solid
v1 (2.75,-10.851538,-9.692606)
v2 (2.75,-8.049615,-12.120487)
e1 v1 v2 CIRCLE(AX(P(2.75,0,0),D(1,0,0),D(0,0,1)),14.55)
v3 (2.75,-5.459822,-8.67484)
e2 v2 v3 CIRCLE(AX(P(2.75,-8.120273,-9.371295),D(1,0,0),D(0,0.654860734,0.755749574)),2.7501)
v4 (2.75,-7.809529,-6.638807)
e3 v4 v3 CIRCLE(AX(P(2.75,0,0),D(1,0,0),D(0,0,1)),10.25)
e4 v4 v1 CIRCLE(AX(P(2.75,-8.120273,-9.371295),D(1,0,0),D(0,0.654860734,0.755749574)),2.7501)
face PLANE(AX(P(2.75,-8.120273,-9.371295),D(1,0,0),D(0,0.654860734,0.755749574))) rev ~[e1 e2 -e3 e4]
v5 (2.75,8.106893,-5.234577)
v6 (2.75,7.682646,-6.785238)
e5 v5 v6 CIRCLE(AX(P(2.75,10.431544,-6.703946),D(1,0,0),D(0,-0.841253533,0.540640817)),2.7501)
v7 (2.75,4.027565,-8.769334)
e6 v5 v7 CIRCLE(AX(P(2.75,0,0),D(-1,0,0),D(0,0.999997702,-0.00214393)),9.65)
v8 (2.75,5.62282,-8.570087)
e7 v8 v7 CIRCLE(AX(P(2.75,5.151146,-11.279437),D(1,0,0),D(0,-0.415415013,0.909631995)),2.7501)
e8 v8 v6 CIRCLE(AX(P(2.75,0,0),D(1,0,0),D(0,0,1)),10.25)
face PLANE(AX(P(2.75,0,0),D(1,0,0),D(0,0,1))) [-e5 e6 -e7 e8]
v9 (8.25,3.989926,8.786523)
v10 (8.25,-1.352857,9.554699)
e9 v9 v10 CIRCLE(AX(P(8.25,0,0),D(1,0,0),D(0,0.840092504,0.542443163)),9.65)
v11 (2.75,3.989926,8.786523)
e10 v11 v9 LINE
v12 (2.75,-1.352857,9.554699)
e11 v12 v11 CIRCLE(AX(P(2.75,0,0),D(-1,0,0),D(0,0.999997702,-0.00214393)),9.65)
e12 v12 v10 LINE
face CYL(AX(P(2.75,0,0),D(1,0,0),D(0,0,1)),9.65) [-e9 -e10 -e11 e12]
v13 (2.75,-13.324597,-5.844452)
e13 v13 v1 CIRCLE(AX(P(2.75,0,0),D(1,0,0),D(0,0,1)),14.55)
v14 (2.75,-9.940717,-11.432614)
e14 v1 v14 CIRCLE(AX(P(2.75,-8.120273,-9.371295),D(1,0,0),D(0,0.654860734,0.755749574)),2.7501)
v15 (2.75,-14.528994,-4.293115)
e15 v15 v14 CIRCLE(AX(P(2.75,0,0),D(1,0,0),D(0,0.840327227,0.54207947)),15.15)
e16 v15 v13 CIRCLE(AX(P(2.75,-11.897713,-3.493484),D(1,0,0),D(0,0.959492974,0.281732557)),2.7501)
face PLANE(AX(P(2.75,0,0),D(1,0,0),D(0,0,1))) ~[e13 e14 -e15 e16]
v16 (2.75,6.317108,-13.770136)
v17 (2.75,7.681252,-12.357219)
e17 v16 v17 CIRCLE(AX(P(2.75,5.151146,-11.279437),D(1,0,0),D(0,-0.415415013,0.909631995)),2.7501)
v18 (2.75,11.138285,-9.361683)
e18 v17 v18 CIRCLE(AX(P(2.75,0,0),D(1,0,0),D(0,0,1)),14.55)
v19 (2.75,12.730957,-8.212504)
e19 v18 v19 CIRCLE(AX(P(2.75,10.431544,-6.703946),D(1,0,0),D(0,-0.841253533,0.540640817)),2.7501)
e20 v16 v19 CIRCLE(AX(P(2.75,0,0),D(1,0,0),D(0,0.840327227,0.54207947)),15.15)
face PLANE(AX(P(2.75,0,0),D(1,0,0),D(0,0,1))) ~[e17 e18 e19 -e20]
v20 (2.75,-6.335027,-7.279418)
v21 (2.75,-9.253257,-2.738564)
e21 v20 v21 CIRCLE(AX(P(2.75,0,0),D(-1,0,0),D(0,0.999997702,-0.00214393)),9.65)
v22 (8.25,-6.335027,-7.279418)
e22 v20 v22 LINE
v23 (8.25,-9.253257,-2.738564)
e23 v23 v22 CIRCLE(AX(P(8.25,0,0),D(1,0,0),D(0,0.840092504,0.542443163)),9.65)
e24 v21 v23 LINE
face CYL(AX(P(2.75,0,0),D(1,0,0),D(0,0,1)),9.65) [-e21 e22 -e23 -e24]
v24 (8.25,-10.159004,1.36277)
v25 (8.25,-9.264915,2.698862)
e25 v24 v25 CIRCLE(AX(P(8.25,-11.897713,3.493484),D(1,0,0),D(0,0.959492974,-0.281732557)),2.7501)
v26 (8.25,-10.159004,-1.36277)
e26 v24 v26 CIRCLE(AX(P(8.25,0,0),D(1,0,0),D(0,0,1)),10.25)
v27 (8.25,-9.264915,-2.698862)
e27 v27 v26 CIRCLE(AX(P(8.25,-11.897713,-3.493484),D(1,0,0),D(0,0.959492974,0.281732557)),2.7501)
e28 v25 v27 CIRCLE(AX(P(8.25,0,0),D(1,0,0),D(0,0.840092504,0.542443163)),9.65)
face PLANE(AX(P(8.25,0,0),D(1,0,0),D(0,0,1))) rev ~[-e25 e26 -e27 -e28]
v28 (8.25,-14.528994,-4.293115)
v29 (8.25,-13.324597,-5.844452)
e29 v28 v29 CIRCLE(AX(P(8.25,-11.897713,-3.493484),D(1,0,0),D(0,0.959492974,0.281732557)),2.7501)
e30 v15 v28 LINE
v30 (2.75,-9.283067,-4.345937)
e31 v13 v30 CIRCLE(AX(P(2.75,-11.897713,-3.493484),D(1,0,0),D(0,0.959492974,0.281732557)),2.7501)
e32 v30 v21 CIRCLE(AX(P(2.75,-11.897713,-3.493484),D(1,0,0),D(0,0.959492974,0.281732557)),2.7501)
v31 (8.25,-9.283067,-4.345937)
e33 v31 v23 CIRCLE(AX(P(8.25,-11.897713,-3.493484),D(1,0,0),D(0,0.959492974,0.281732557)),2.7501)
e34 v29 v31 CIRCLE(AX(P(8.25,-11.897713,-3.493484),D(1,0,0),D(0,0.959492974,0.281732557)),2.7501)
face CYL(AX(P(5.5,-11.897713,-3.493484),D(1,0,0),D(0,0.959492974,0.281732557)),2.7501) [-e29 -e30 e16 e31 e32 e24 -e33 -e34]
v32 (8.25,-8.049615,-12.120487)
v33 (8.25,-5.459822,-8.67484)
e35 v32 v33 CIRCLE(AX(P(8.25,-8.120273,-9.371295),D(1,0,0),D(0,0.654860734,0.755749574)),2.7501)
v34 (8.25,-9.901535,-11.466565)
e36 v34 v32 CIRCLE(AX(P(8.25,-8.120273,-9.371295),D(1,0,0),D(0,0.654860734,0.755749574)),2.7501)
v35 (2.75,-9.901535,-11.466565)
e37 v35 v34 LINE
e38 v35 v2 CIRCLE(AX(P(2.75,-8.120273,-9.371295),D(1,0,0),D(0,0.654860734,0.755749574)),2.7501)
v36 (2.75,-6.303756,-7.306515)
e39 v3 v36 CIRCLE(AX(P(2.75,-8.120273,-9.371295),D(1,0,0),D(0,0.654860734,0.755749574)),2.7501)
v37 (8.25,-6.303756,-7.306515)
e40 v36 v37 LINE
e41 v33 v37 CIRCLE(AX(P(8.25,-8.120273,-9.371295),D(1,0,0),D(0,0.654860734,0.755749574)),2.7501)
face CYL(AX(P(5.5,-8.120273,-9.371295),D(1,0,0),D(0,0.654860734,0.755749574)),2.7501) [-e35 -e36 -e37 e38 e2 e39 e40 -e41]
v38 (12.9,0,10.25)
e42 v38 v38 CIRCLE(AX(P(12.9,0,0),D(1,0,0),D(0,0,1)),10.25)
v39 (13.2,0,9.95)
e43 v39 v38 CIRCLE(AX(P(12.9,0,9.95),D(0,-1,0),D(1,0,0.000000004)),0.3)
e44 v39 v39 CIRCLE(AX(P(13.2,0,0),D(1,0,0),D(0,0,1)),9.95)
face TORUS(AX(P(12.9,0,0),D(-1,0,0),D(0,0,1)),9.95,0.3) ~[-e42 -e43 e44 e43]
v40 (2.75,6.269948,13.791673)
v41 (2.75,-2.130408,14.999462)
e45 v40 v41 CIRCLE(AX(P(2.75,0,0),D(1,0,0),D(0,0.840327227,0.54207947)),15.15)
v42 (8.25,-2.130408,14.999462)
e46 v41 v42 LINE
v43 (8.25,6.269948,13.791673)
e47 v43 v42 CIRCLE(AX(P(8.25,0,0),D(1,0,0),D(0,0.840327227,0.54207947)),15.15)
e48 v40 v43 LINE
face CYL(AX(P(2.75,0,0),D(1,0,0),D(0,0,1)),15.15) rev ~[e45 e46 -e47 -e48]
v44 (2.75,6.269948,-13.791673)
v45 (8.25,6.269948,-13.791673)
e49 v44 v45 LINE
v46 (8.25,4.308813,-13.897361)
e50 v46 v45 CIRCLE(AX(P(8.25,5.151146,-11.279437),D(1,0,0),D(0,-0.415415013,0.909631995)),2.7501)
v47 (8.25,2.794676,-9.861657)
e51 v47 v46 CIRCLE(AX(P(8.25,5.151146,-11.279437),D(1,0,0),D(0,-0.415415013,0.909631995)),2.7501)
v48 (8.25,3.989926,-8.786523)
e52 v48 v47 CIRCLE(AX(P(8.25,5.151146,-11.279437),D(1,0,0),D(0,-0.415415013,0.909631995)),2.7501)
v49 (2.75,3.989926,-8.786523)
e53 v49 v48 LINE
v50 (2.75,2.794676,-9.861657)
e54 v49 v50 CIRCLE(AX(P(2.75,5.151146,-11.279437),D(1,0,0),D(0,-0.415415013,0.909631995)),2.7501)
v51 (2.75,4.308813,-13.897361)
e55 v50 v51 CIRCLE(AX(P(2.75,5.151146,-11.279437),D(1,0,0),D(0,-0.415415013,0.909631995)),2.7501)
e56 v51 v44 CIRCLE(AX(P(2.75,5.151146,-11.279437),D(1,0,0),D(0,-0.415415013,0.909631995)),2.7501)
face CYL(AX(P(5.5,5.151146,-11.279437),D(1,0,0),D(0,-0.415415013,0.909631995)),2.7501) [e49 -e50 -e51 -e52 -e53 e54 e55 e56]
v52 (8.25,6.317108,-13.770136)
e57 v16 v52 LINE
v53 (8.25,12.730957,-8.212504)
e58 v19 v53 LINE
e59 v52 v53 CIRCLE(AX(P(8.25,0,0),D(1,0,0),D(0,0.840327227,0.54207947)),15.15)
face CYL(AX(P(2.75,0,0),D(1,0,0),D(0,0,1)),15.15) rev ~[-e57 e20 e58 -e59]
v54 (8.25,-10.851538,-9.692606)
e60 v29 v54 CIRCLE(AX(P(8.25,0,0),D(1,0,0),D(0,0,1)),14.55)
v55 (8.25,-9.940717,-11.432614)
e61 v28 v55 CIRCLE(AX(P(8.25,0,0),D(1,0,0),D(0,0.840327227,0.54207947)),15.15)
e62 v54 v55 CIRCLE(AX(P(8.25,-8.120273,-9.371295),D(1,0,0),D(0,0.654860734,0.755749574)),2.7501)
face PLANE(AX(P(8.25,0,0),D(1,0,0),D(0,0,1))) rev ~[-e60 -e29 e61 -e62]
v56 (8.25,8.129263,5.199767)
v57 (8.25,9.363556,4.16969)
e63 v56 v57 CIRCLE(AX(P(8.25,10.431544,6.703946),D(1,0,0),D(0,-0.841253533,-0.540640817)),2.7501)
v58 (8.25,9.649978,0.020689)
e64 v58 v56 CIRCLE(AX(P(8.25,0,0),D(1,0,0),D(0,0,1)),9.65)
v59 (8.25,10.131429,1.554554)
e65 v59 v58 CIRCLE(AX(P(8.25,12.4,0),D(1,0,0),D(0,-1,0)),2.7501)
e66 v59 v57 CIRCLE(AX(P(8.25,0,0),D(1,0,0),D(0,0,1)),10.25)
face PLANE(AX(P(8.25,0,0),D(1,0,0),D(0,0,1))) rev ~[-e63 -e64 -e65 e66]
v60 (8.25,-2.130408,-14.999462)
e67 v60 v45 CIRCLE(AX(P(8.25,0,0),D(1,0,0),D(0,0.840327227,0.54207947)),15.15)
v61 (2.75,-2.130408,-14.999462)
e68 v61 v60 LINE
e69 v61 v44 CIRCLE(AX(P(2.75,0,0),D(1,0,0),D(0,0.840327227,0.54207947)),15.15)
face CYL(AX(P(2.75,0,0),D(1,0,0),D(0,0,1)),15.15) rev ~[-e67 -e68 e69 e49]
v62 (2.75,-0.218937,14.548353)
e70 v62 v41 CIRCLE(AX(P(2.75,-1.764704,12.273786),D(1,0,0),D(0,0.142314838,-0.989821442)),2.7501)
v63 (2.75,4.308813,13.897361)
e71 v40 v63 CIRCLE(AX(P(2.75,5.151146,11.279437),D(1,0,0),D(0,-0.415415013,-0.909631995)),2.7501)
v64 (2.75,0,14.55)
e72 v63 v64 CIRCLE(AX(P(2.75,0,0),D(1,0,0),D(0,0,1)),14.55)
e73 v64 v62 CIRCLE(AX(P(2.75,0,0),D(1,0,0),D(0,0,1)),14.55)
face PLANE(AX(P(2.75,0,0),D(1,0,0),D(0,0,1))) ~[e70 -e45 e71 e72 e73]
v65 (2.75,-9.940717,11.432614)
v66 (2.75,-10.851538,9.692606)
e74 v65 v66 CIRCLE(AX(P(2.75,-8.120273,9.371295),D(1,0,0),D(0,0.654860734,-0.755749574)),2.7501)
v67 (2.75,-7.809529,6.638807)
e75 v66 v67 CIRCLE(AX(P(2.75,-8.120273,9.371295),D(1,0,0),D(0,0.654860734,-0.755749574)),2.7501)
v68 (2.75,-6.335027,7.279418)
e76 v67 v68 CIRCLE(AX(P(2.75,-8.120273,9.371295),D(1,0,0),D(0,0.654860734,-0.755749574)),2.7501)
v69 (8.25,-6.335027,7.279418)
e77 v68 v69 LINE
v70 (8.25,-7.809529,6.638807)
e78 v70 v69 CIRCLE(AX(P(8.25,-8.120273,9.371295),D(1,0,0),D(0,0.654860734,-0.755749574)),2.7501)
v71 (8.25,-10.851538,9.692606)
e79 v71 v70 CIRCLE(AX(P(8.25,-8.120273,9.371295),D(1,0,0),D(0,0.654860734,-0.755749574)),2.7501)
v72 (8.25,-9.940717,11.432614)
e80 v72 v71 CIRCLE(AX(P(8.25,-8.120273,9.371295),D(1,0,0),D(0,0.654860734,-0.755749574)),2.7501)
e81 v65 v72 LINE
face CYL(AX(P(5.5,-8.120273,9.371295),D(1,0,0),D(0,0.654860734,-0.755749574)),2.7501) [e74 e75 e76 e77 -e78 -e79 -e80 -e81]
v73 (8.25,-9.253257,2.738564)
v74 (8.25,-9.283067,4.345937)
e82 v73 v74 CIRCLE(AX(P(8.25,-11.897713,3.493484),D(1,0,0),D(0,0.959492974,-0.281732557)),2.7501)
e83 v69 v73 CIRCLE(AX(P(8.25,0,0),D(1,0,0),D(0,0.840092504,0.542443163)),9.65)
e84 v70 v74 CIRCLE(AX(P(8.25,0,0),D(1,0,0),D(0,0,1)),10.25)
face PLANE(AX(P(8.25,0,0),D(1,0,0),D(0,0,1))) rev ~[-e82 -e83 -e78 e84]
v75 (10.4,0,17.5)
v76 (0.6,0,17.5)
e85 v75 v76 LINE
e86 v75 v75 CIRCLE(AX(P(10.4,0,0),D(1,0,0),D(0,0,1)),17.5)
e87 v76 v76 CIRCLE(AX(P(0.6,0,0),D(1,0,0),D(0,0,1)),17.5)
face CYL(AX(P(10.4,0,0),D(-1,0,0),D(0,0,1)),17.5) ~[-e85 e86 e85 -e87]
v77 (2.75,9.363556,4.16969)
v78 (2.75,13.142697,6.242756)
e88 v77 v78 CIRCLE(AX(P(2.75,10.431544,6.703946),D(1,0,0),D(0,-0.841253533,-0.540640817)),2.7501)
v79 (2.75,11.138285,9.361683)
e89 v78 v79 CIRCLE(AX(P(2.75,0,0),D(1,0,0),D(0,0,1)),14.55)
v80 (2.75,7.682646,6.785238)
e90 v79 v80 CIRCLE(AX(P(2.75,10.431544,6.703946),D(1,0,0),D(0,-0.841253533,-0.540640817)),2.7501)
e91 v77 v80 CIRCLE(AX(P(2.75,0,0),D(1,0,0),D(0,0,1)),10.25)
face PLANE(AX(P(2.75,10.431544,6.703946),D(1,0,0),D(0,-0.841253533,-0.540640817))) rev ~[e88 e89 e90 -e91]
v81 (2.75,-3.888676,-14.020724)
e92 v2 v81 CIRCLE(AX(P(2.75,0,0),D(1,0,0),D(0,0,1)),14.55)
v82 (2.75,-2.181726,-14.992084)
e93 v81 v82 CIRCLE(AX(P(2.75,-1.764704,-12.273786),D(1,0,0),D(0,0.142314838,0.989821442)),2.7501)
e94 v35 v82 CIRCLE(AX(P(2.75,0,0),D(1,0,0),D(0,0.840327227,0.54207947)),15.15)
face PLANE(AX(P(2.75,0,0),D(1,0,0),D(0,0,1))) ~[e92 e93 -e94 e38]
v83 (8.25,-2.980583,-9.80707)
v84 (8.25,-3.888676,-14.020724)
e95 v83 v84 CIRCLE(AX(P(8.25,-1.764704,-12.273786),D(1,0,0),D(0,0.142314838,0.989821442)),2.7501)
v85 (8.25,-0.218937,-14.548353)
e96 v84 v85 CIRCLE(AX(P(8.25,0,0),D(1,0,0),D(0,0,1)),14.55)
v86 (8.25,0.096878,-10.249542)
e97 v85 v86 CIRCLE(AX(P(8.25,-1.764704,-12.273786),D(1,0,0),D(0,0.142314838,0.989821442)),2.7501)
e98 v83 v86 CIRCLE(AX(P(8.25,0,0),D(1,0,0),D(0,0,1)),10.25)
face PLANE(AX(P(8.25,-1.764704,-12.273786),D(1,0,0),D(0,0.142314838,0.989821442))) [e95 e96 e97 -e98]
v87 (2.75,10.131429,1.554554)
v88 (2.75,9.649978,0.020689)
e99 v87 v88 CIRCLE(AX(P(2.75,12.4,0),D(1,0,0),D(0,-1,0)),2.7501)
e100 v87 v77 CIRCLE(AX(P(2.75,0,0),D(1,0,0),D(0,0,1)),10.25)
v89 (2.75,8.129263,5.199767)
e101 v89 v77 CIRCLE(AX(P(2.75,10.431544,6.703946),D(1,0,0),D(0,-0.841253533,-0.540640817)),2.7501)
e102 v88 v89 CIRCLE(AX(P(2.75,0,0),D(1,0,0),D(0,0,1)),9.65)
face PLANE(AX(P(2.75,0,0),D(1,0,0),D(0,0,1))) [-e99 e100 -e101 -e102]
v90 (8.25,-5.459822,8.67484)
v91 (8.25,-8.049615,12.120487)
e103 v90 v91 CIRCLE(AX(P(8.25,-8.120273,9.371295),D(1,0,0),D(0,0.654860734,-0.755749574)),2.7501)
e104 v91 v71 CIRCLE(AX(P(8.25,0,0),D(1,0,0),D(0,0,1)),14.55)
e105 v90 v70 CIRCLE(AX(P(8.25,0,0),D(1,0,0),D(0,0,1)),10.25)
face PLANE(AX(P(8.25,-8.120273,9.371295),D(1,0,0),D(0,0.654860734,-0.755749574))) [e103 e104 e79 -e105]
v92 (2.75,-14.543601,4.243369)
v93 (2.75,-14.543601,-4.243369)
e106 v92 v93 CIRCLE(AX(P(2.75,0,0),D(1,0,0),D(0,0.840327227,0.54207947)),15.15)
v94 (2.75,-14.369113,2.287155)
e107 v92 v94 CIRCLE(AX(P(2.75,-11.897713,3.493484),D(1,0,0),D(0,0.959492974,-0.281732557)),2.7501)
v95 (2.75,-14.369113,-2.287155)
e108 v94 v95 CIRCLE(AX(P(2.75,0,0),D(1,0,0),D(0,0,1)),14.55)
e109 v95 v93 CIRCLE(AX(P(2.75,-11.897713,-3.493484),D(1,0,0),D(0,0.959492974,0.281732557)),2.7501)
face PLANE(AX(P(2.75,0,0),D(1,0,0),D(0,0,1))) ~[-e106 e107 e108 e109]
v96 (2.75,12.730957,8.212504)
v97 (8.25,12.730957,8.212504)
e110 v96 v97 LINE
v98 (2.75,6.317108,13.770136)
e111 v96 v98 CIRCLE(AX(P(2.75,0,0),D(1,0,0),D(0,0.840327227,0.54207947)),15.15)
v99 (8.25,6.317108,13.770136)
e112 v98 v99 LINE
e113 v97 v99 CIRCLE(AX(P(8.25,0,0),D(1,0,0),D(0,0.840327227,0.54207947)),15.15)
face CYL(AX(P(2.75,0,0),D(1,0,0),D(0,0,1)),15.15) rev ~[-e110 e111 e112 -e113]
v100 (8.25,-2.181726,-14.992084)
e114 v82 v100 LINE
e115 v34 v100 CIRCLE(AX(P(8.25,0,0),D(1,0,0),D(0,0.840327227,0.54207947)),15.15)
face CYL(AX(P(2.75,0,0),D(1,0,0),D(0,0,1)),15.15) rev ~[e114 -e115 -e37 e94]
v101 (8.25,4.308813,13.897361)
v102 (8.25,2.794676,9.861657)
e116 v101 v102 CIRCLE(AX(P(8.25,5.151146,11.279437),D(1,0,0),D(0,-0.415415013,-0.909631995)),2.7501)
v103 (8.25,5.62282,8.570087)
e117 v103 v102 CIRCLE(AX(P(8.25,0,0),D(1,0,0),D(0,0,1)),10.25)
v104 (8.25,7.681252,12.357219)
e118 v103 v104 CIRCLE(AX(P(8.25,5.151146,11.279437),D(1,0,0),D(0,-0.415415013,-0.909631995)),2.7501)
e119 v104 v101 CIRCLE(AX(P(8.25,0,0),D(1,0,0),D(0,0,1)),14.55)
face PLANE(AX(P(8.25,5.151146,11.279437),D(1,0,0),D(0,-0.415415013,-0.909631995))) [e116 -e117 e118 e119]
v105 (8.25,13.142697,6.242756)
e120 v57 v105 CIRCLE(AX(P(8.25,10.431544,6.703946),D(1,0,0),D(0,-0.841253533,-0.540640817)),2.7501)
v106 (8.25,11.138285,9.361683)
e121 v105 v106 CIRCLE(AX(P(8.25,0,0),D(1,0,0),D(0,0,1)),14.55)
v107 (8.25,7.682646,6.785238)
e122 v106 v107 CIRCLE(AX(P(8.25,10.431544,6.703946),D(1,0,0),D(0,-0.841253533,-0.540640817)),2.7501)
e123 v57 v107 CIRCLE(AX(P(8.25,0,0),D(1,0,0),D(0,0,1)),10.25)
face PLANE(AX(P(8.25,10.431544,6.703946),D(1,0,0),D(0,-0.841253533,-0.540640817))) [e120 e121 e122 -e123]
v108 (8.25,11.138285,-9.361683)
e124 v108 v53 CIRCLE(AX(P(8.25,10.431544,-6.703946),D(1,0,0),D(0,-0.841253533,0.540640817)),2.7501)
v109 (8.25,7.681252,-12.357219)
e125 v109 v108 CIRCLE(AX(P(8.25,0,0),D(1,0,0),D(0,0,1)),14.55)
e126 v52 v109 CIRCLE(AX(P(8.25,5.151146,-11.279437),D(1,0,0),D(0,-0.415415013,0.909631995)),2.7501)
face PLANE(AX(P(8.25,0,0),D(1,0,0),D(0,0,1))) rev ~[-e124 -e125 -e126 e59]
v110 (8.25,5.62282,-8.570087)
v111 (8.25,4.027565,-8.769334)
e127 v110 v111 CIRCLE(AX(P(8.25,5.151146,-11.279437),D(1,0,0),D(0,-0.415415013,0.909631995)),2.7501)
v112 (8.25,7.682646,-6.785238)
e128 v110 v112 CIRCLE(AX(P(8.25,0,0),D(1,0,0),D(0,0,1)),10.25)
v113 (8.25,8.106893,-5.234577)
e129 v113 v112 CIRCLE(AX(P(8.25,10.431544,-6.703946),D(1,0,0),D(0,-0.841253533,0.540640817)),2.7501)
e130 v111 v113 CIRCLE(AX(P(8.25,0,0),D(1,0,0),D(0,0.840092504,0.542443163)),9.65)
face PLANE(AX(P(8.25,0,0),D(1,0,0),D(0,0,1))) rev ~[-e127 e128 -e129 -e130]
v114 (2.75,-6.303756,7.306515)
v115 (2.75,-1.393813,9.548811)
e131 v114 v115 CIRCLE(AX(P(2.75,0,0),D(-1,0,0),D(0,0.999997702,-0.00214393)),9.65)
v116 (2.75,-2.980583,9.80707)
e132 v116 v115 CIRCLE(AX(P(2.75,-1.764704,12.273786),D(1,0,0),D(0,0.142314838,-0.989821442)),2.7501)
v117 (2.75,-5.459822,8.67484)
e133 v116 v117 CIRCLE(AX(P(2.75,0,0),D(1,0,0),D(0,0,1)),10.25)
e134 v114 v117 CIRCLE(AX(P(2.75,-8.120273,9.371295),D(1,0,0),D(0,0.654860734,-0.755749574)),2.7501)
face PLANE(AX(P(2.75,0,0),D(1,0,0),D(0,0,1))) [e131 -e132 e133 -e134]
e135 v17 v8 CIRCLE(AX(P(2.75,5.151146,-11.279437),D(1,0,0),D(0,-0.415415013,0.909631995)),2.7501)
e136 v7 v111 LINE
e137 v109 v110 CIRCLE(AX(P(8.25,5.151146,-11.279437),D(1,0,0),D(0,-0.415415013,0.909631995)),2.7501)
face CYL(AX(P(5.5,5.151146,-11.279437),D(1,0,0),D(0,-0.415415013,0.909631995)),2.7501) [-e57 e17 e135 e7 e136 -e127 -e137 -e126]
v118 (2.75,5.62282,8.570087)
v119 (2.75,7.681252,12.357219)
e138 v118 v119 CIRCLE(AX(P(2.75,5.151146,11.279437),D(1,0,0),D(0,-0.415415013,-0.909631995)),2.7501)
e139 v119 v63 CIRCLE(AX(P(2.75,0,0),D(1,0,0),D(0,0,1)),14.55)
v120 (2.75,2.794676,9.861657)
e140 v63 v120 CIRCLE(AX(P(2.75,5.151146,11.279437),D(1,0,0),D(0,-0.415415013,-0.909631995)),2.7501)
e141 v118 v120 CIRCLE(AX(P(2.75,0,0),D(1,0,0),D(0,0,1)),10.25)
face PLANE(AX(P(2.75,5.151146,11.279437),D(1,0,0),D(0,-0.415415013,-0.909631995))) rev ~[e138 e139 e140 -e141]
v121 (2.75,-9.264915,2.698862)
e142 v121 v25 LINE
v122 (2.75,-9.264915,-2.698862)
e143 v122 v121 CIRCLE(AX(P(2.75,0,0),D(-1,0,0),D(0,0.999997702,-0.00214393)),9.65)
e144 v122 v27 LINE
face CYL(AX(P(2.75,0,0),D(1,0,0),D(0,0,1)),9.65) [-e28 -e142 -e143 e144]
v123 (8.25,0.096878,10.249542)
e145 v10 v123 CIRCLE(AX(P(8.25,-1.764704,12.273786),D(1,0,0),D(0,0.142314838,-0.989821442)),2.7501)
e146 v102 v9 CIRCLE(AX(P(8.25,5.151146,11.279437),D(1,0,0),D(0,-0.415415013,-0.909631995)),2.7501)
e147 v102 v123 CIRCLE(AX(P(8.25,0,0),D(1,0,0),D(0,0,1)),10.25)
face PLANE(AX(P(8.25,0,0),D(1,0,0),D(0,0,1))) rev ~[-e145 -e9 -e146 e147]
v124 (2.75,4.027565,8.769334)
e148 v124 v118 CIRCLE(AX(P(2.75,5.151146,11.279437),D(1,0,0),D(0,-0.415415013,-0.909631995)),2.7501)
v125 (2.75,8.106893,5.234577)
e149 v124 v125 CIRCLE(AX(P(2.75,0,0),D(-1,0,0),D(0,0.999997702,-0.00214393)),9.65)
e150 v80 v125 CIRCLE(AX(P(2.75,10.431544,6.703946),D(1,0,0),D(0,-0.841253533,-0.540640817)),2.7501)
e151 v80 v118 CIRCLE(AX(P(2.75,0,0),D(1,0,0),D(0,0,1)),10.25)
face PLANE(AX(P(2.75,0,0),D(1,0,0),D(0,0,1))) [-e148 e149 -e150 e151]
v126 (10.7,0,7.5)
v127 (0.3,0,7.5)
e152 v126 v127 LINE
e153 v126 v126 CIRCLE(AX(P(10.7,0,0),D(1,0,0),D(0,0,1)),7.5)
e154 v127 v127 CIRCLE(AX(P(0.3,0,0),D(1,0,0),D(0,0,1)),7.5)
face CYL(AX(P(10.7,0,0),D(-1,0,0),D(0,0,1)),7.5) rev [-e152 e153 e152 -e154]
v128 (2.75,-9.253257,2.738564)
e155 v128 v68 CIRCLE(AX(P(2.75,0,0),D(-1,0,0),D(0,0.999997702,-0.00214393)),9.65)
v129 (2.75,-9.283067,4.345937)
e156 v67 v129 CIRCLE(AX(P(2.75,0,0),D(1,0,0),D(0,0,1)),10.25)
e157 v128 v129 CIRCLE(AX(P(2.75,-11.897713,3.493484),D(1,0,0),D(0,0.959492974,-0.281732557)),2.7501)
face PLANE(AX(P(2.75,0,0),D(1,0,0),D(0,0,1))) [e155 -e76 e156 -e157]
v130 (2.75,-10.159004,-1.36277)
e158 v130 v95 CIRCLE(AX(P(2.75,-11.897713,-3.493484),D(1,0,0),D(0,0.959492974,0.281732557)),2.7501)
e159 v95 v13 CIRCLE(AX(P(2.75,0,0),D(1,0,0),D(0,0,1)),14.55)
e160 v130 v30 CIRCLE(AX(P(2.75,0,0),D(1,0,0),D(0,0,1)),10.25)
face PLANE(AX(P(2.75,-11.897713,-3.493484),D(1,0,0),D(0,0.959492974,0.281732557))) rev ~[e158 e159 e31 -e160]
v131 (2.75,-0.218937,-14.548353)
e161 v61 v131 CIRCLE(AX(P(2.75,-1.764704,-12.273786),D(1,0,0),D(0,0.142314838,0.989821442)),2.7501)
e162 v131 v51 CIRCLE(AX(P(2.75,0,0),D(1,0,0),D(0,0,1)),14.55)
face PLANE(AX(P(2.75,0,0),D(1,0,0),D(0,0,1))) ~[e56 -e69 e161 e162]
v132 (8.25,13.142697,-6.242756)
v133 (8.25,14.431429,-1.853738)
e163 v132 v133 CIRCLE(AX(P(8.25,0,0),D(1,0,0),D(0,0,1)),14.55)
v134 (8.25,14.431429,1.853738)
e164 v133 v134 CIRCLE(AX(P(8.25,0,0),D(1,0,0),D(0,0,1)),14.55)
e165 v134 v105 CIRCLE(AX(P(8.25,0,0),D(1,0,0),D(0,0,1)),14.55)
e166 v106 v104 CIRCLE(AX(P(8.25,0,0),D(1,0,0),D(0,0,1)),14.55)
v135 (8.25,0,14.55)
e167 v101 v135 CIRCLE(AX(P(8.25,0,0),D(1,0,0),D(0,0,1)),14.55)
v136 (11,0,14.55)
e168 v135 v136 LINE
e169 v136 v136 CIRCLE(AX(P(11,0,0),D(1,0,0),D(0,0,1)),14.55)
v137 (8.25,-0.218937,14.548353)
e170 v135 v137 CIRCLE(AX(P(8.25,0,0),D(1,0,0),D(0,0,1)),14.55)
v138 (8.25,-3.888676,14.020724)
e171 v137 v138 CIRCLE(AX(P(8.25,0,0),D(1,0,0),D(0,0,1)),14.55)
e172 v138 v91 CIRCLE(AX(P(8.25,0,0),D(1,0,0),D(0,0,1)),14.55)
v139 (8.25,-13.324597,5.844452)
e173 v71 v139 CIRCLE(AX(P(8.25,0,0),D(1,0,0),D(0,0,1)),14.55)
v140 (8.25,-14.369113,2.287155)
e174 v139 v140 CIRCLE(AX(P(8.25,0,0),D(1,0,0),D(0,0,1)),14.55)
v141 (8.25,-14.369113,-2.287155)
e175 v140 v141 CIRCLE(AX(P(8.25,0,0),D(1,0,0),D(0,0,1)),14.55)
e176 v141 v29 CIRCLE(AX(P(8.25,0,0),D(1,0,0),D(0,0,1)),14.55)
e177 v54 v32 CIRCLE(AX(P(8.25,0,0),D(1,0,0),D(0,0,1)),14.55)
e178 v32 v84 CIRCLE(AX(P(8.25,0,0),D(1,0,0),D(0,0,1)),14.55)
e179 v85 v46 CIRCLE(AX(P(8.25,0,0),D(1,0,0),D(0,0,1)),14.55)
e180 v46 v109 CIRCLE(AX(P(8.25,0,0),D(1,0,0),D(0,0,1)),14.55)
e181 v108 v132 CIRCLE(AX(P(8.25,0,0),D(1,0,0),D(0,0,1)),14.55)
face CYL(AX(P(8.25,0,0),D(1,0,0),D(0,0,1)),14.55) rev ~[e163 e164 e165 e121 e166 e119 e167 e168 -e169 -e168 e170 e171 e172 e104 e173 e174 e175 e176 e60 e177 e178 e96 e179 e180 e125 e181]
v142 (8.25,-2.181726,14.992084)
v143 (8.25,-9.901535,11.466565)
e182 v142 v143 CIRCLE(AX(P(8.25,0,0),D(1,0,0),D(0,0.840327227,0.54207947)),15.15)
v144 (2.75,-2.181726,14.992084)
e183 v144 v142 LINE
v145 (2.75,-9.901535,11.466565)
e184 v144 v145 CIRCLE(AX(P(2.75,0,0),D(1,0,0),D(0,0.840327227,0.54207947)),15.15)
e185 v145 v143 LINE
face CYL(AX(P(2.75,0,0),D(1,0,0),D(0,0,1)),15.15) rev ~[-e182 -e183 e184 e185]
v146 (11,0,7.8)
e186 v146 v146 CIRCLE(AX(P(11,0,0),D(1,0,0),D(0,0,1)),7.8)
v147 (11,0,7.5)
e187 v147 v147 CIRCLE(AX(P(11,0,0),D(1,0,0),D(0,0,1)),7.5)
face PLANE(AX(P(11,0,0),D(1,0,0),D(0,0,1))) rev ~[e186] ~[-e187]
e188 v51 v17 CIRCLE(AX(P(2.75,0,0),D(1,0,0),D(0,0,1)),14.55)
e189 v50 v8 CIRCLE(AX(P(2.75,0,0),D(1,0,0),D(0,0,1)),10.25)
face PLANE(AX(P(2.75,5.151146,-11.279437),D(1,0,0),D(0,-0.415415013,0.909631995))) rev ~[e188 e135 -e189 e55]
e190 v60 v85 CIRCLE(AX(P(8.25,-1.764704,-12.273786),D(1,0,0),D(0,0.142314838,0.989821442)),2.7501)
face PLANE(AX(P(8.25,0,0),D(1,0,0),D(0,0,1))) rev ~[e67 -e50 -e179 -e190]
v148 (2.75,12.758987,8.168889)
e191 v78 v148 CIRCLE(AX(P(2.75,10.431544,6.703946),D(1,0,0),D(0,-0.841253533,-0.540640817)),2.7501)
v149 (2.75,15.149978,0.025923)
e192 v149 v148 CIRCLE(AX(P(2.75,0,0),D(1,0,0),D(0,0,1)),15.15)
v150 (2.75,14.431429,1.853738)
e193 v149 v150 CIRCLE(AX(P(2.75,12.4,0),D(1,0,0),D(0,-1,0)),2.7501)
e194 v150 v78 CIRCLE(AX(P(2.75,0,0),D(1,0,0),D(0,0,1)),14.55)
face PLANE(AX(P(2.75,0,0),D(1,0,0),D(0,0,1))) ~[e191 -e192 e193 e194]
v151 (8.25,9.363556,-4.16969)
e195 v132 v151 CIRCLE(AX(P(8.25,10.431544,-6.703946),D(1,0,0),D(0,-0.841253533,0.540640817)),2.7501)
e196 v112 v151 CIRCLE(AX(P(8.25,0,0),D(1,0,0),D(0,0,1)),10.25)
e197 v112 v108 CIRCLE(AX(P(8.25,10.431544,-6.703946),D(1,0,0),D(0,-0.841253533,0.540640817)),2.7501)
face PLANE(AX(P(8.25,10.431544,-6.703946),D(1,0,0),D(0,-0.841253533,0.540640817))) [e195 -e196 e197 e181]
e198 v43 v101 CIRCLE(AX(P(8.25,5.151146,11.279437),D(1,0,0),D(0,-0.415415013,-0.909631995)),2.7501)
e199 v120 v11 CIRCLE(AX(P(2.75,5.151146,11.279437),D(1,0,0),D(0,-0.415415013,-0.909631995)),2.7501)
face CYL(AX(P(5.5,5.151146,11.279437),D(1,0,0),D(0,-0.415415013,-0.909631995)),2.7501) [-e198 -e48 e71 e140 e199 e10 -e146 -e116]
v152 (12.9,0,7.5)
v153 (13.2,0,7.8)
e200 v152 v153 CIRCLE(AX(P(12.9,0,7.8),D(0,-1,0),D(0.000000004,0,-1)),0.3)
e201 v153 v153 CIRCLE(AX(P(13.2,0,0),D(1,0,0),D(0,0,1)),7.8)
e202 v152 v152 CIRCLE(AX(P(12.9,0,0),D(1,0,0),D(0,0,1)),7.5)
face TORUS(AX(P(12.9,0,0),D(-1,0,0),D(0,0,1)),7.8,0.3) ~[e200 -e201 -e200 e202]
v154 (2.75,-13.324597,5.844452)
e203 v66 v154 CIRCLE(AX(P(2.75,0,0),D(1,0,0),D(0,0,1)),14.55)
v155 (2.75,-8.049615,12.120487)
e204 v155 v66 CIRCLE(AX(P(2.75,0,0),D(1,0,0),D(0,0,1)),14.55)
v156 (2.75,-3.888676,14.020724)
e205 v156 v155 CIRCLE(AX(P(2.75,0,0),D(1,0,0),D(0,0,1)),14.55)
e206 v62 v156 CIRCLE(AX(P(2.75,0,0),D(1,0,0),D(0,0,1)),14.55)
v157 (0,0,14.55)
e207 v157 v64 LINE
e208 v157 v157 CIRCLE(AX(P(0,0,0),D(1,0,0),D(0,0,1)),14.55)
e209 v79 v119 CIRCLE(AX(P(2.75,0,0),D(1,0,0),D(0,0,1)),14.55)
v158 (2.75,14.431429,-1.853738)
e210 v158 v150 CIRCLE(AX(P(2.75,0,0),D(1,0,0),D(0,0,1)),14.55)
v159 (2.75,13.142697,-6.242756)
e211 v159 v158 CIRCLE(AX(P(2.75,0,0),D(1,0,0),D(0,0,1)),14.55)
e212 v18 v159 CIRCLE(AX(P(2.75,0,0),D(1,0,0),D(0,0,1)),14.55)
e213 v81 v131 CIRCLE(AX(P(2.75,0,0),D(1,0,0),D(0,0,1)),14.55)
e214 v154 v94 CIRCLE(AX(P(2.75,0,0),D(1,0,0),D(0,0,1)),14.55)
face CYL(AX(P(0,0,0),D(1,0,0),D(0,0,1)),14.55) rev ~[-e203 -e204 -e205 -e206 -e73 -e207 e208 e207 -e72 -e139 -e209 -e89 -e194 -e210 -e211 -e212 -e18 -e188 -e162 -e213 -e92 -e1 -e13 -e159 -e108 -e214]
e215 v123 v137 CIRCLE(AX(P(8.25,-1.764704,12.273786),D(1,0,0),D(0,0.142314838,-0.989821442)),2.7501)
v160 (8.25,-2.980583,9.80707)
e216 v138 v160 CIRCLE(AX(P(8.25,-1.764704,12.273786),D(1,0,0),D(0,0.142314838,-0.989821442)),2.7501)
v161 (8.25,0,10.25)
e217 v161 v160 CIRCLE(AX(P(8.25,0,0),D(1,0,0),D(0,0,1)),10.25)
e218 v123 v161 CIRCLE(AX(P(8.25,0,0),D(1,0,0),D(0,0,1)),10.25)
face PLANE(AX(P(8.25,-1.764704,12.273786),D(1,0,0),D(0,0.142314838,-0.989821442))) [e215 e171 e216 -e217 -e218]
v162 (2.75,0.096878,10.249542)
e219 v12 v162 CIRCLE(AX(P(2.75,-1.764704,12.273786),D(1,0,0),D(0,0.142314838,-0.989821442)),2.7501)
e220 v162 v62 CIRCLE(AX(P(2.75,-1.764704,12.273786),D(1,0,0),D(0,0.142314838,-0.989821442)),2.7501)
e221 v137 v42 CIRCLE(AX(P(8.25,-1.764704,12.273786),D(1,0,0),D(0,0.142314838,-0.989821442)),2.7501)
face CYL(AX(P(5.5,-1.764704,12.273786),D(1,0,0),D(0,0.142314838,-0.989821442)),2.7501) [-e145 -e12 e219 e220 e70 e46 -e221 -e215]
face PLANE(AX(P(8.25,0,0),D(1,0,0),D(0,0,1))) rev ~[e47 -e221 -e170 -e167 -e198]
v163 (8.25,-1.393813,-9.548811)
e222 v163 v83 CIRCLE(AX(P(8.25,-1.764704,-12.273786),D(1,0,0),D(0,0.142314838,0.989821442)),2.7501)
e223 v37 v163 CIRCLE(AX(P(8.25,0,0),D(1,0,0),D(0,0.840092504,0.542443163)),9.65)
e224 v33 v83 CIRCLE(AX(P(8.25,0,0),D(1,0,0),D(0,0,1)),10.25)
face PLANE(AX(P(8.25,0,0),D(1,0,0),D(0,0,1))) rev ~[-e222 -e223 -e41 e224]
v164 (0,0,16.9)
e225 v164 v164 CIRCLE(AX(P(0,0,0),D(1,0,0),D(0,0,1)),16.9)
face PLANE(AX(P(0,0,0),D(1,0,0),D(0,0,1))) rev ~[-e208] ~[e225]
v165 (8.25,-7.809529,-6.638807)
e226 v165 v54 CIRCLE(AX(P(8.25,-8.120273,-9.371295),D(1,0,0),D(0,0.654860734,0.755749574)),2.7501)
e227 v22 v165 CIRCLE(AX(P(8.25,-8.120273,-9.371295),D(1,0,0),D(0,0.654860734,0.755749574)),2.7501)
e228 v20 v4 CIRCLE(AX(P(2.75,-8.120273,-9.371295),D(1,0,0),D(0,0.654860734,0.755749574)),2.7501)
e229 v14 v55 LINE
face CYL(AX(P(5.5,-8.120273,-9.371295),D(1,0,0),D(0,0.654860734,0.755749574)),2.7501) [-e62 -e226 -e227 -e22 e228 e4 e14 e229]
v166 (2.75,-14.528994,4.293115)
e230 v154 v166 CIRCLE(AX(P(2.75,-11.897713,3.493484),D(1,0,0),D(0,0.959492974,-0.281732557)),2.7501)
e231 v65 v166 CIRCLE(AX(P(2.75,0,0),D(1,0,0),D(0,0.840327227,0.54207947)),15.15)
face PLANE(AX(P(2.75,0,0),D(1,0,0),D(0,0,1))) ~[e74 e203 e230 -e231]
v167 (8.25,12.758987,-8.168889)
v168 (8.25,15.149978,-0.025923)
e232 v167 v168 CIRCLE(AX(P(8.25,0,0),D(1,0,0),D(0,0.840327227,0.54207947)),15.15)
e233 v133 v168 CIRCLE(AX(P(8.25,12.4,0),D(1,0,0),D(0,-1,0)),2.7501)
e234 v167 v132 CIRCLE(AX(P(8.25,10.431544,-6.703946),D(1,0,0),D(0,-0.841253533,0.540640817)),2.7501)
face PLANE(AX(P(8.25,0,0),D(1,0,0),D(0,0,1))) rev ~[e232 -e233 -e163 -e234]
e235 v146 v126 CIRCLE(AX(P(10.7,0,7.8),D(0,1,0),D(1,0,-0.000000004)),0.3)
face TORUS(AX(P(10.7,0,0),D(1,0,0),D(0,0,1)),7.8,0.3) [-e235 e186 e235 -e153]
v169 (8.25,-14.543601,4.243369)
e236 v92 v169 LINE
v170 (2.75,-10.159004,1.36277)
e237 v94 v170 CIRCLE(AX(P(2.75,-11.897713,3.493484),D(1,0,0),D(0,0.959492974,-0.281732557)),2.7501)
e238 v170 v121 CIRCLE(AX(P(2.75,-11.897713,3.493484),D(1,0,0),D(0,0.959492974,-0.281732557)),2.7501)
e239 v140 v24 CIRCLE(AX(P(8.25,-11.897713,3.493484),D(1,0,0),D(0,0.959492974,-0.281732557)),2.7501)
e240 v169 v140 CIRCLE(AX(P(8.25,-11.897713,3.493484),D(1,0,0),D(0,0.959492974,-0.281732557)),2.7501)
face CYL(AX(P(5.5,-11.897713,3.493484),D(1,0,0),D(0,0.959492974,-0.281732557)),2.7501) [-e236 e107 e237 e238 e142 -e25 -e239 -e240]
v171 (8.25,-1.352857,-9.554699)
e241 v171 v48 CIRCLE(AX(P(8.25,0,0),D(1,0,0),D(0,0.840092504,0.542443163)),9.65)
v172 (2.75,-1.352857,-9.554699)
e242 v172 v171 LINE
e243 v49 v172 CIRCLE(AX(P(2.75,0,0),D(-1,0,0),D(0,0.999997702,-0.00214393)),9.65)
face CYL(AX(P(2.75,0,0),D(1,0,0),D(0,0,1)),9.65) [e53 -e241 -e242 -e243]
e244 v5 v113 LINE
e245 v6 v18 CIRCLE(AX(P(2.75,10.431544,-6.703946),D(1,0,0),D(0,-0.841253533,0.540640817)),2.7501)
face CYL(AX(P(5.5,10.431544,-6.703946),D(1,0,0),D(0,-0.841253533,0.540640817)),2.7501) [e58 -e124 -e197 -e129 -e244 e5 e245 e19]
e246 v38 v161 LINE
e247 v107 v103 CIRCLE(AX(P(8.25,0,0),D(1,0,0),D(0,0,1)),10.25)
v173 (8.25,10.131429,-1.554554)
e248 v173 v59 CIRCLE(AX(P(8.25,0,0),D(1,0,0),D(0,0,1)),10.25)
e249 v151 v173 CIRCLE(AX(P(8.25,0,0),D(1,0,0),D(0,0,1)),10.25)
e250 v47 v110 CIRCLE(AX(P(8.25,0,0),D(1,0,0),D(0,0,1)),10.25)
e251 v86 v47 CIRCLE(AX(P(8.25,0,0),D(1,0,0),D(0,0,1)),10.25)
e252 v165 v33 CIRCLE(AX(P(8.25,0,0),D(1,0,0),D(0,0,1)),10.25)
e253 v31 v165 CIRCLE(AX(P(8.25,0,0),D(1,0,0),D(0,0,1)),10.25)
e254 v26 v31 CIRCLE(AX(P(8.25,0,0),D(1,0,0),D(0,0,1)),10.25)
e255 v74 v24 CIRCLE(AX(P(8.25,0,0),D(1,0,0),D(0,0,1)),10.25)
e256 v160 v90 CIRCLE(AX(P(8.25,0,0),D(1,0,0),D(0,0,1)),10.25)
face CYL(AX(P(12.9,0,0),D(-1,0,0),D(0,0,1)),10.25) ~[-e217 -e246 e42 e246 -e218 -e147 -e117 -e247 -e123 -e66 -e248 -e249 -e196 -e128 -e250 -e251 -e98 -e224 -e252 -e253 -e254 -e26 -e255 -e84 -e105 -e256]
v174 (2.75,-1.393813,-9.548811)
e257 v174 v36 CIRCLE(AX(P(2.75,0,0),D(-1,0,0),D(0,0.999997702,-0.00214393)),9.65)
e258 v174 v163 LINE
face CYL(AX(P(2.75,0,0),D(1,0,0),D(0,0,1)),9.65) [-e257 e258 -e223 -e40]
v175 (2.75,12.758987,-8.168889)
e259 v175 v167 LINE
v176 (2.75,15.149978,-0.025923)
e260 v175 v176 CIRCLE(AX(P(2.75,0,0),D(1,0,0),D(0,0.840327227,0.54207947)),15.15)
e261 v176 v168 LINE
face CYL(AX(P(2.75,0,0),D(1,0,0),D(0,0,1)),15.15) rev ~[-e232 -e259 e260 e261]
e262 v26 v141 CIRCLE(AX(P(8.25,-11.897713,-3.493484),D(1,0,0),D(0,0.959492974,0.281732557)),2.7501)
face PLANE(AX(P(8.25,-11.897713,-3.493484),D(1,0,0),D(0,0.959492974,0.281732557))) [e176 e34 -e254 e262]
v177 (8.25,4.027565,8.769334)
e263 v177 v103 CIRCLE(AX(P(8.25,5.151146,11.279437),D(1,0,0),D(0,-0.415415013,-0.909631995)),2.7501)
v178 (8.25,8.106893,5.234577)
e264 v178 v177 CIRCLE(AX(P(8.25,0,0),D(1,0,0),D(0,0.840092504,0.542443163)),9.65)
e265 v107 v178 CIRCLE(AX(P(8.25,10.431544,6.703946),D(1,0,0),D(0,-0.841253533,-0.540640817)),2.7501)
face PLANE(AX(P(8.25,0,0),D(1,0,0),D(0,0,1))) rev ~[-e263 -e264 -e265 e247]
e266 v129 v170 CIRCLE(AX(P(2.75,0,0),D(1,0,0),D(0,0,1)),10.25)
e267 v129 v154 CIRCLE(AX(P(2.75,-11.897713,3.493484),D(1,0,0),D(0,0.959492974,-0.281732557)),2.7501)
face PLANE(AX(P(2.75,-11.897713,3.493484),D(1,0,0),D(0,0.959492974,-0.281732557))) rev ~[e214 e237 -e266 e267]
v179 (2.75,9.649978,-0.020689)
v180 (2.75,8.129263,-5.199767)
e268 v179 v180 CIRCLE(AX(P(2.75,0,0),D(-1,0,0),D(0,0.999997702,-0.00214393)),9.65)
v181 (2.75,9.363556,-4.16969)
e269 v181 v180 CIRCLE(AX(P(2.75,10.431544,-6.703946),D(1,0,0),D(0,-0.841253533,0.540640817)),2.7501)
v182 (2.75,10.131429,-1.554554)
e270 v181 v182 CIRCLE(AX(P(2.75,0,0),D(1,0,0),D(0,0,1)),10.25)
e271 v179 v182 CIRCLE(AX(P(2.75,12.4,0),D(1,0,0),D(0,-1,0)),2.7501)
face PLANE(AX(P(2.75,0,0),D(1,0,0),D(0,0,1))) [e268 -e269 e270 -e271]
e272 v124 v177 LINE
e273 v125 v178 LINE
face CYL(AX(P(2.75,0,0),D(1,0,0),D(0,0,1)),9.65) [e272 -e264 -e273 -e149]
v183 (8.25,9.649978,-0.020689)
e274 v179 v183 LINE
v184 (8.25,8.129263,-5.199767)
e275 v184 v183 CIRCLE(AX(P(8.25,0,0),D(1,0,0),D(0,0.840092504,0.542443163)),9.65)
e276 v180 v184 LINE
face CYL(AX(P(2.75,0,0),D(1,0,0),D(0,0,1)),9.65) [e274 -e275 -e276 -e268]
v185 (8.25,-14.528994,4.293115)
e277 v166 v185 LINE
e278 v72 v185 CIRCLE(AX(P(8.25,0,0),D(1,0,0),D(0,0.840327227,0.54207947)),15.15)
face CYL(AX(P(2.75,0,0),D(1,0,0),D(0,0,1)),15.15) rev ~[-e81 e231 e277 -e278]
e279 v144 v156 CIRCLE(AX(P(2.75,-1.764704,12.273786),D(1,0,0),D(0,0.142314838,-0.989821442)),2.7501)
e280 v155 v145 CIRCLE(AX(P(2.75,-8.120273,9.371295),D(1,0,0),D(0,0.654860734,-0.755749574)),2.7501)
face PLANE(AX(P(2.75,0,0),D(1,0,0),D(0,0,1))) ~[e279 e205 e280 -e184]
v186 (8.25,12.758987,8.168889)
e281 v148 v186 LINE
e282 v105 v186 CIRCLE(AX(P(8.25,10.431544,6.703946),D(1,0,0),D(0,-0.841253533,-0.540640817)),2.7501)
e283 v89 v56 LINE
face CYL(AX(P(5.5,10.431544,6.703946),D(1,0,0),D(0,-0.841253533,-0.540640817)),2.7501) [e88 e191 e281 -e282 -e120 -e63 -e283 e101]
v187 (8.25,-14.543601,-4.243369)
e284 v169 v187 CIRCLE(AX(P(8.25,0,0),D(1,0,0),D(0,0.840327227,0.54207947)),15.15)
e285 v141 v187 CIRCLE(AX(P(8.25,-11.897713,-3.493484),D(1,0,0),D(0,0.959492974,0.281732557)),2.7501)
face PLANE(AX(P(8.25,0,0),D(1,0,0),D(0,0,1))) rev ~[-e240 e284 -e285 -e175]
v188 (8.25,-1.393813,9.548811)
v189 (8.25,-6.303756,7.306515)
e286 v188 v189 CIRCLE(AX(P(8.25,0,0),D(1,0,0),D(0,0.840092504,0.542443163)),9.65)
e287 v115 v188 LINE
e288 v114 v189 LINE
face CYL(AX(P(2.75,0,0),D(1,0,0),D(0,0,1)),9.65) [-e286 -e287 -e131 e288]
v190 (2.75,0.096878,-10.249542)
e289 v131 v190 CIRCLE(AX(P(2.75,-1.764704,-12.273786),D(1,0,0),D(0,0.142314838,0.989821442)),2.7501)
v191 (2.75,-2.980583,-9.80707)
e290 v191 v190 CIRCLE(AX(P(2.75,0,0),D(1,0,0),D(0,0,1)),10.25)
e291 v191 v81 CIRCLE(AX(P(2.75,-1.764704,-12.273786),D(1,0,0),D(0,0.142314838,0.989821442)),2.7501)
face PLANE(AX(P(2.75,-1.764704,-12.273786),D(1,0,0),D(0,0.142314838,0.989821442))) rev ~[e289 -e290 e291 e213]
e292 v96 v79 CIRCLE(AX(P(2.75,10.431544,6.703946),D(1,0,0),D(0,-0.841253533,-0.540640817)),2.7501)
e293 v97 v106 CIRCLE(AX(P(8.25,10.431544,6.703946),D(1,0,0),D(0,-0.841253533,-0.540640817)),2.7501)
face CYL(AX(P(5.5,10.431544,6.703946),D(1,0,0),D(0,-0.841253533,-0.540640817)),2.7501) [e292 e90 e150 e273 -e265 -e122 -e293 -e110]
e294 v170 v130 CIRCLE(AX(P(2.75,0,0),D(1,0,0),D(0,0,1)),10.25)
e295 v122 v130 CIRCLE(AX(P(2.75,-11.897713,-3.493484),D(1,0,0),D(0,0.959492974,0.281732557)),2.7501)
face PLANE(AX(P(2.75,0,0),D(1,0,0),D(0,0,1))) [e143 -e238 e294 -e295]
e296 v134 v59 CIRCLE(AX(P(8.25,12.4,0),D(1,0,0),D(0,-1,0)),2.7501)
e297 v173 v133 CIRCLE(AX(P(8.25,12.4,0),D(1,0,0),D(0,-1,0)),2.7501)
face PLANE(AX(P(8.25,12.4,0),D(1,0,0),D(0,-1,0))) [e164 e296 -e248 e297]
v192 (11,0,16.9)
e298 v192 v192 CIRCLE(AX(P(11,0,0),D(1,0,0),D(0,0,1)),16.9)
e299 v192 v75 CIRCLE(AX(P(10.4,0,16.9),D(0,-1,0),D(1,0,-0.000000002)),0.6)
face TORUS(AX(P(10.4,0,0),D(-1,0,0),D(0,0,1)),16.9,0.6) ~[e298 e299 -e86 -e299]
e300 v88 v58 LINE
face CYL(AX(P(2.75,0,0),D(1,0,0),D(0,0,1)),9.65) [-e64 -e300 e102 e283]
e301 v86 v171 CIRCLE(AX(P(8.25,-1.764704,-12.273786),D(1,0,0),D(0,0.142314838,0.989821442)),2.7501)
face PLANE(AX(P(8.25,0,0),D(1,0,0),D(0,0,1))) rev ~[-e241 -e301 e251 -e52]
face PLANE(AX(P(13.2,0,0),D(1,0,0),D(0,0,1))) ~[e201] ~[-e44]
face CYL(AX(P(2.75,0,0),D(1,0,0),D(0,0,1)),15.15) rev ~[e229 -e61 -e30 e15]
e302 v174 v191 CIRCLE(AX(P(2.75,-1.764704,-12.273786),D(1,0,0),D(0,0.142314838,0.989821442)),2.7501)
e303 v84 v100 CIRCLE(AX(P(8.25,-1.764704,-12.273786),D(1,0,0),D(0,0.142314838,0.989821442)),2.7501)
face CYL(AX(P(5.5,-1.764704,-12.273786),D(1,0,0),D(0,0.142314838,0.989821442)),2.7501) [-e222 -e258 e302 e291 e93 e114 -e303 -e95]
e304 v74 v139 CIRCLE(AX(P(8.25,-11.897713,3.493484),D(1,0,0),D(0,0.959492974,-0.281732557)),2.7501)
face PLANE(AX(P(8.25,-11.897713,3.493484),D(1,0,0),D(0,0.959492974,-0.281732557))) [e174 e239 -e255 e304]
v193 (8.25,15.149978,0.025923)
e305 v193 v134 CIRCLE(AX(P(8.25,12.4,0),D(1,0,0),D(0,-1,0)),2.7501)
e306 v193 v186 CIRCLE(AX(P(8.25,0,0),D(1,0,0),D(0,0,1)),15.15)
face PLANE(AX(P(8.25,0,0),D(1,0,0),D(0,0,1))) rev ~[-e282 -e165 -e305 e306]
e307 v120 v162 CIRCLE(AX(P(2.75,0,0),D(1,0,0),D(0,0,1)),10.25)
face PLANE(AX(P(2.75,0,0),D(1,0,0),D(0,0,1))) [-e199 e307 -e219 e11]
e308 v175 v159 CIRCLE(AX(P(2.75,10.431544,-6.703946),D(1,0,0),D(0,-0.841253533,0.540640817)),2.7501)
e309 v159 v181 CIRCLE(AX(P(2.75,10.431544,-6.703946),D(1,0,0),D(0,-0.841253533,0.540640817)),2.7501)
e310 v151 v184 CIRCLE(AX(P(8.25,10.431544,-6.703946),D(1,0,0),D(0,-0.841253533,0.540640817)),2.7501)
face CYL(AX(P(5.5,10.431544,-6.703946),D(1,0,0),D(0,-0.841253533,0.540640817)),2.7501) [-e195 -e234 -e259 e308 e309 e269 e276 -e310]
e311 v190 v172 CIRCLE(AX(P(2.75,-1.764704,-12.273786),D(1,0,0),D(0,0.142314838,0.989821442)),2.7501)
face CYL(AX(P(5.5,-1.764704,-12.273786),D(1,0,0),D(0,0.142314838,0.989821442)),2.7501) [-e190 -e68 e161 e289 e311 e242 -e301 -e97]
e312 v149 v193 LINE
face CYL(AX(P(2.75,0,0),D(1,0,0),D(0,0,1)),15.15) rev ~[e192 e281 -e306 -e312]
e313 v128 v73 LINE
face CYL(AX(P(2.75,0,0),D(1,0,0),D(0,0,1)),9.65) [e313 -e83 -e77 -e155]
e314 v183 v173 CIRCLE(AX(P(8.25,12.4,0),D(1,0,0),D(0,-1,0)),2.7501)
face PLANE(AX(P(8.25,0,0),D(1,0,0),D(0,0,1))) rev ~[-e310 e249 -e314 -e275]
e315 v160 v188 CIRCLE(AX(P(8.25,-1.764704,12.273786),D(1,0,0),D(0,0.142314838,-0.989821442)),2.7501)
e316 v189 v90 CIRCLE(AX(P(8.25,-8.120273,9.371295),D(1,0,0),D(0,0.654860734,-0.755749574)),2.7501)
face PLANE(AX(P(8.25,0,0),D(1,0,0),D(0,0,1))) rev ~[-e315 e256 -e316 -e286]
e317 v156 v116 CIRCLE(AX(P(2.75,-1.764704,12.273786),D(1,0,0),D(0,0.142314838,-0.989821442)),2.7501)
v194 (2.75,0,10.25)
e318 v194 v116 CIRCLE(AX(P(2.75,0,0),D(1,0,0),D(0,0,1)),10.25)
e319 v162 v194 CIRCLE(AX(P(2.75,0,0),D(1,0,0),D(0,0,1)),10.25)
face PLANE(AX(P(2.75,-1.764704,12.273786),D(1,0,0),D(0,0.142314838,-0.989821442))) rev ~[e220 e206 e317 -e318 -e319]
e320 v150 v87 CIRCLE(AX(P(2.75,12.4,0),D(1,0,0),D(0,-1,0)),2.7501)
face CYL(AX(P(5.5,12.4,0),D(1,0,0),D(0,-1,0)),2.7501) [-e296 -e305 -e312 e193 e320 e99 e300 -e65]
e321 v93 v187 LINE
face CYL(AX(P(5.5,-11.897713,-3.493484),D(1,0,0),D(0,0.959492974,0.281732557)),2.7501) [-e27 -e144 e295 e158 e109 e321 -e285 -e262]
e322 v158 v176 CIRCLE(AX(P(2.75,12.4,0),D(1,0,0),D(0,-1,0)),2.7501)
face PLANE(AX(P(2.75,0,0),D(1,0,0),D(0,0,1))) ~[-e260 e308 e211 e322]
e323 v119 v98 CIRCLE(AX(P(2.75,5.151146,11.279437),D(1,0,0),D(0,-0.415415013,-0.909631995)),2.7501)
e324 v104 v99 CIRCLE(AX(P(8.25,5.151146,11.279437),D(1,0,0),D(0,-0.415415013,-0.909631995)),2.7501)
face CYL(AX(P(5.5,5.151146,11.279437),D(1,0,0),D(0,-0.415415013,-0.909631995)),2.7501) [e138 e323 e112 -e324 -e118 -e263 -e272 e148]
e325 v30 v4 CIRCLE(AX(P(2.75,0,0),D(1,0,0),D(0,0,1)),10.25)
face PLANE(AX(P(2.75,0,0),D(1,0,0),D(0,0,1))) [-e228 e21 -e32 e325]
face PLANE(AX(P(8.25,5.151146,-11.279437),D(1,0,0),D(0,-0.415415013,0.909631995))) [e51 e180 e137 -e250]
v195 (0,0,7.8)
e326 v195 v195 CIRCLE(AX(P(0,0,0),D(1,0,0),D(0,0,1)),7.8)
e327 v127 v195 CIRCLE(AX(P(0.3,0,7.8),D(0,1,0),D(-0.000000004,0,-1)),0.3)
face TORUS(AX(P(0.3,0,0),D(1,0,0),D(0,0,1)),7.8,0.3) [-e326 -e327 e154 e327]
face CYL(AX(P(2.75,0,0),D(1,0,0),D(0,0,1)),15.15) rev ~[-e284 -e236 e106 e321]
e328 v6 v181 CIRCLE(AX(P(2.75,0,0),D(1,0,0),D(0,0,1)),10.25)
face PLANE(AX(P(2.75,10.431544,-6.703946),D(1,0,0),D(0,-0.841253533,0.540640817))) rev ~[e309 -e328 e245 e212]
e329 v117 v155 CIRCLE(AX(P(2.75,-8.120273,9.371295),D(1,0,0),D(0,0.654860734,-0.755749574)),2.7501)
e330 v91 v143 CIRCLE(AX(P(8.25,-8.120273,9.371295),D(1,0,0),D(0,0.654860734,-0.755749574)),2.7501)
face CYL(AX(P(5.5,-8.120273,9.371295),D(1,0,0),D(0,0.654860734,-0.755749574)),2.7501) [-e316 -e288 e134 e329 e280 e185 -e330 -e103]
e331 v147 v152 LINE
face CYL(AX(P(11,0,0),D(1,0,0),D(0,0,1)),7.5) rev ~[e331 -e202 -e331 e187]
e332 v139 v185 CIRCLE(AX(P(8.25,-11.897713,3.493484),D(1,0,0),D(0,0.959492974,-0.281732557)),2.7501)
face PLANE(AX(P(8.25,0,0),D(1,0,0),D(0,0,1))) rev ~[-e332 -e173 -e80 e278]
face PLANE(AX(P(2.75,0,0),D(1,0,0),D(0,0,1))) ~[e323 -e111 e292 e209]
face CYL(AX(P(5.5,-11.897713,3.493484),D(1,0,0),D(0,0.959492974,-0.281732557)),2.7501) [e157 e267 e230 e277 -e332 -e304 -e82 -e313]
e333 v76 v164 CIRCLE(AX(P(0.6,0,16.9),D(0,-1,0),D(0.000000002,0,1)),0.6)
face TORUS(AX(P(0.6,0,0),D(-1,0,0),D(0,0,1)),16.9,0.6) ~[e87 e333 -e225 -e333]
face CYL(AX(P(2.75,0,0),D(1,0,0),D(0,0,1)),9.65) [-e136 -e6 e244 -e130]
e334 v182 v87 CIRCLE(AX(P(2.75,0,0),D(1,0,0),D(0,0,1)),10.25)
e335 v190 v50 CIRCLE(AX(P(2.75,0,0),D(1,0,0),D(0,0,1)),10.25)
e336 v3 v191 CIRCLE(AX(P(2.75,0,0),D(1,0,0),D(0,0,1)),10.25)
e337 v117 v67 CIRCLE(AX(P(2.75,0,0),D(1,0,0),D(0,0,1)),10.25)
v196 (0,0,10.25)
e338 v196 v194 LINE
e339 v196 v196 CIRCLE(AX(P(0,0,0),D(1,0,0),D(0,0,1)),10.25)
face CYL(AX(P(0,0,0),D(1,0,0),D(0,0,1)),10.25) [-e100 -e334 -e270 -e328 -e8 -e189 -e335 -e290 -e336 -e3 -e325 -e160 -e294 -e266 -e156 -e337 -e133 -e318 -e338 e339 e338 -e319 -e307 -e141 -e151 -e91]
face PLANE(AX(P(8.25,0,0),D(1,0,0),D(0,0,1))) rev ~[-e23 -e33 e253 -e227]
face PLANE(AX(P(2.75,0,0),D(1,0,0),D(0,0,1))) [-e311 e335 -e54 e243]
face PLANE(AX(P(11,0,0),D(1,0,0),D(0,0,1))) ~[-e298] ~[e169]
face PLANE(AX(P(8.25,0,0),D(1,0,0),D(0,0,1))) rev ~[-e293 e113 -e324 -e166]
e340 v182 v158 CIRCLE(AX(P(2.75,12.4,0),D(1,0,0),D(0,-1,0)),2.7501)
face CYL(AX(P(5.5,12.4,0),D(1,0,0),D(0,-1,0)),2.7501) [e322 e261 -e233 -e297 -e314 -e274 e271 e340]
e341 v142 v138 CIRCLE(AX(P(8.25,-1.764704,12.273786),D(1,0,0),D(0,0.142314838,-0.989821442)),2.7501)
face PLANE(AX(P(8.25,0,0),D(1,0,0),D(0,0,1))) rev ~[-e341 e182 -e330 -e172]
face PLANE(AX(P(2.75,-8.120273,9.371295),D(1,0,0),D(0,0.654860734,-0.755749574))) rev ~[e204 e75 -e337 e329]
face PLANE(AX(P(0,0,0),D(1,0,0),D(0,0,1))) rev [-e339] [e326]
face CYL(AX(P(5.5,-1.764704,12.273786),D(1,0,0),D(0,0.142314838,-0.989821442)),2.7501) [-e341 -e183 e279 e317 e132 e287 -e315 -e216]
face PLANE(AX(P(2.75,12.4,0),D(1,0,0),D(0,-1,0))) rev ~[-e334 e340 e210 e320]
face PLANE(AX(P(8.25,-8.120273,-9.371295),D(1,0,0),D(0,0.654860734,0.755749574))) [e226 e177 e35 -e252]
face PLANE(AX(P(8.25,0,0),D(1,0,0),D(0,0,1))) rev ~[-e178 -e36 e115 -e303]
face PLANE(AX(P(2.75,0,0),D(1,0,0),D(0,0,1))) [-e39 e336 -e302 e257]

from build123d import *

# Parameters (mm, degrees)
SKETCH_3_W               = 5.5
SKETCH_3_H               = 2.7501
PATTERN_CIRCULAR_1_COUNT = 11


with BuildPart() as part:
    # 草图2 → Revolve 794 (revolve)
    with BuildSketch(Plane.XY, mode=Mode.PRIVATE) as revolve_794_sk:
        with BuildLine():
            Line((2.75, 9.65), (8.25, 9.65))
            Line((8.25, 9.65), (11, 8.913139721))
            Line((11, 8.913139721), (11, 7.8))
            ThreePointArc((11, 7.8), (10.912132034, 7.587867966), (10.7, 7.5))
            Line((10.7, 7.5), (0.3, 7.5))
            ThreePointArc((0.3, 7.5), (0.087867966, 7.587867966), (0, 7.8))
            Line((0, 7.8), (0, 10.25))
            Line((0, 10.25), (2.75, 10.25))
            Line((2.75, 10.25), (2.75, 9.65))
        make_face()
    revolve(revolve_794_sk.sketch.rotate(Axis((-10.080094127, 0, 0), (1, 0, 0)), 90), axis=Axis((-10.080094127, 0, 0), (1, 0, 0)))

    # 草图3 → 凸台-旋转1 (revolve)
    with BuildSketch(Plane.XY):
        with Locations((5.5, 11.02495)):
            Rectangle(SKETCH_3_W, SKETCH_3_H)
    revolve_1 = revolve(axis=Axis((-1.603948851, 12.4, 0), (1, 0, 0)))

    # 草图4 → 凸台-旋转2 (revolve)
    with BuildSketch(Plane.XY, mode=Mode.PRIVATE) as revolve_2_sk:
        with BuildLine():
            Line((8.25, 14.55), (11, 14.55))
            Line((11, 14.55), (11, 16.9))
            ThreePointArc((11, 16.9), (10.824264069, 17.324264069), (10.4, 17.5))
            Line((10.4, 17.5), (0.6, 17.5))
            ThreePointArc((0.6, 17.5), (0.175735931, 17.324264069), (0, 16.9))
            Line((0, 16.9), (0, 14.55))
            Line((0, 14.55), (2.75, 14.55))
            Line((2.75, 14.55), (2.75, 15.15))
            Line((2.75, 15.15), (8.25, 15.15))
            Line((8.25, 15.15), (8.25, 14.55))
        make_face()
    revolve(revolve_2_sk.sketch.rotate(Axis((0, 0, 0), (1, 0, 0)), 90), axis=Axis((0, 0, 0), (1, 0, 0)))

    # 草图5 → 凸台-旋转3 (revolve)
    with BuildSketch(Plane.XY, mode=Mode.PRIVATE) as revolve_3_sk:
        with BuildLine():
            Line((11, 8.913117543), (11, 7.5))
            Line((11, 7.5), (12.9, 7.5))
            ThreePointArc((12.9, 7.5), (13.112132034, 7.587867966), (13.2, 7.8))
            Line((13.2, 7.8), (13.2, 9.95))
            ThreePointArc((13.2, 9.95), (13.112132034, 10.162132034), (12.9, 10.25))
            Line((12.9, 10.25), (8.25, 10.25))
            Line((8.25, 10.25), (8.25, 9.649977822))
            Line((8.25, 9.649977822), (11, 8.913117543))
        make_face()
    revolve(revolve_3_sk.sketch.rotate(Axis((0, 0, 0), (1, 0, 0)), 90), axis=Axis((0, 0, 0), (1, 0, 0)))

    # 阵列(圆周)1: 凸台-旋转1 ×11 about axis
    pattern_circular_1_axis = Axis((0, 0, 0), (1, 0, 0))
    for i in range(1, PATTERN_CIRCULAR_1_COUNT):
        add(revolve_1.rotate(pattern_circular_1_axis, i * 360 / PATTERN_CIRCULAR_1_COUNT))


solid = part.part
